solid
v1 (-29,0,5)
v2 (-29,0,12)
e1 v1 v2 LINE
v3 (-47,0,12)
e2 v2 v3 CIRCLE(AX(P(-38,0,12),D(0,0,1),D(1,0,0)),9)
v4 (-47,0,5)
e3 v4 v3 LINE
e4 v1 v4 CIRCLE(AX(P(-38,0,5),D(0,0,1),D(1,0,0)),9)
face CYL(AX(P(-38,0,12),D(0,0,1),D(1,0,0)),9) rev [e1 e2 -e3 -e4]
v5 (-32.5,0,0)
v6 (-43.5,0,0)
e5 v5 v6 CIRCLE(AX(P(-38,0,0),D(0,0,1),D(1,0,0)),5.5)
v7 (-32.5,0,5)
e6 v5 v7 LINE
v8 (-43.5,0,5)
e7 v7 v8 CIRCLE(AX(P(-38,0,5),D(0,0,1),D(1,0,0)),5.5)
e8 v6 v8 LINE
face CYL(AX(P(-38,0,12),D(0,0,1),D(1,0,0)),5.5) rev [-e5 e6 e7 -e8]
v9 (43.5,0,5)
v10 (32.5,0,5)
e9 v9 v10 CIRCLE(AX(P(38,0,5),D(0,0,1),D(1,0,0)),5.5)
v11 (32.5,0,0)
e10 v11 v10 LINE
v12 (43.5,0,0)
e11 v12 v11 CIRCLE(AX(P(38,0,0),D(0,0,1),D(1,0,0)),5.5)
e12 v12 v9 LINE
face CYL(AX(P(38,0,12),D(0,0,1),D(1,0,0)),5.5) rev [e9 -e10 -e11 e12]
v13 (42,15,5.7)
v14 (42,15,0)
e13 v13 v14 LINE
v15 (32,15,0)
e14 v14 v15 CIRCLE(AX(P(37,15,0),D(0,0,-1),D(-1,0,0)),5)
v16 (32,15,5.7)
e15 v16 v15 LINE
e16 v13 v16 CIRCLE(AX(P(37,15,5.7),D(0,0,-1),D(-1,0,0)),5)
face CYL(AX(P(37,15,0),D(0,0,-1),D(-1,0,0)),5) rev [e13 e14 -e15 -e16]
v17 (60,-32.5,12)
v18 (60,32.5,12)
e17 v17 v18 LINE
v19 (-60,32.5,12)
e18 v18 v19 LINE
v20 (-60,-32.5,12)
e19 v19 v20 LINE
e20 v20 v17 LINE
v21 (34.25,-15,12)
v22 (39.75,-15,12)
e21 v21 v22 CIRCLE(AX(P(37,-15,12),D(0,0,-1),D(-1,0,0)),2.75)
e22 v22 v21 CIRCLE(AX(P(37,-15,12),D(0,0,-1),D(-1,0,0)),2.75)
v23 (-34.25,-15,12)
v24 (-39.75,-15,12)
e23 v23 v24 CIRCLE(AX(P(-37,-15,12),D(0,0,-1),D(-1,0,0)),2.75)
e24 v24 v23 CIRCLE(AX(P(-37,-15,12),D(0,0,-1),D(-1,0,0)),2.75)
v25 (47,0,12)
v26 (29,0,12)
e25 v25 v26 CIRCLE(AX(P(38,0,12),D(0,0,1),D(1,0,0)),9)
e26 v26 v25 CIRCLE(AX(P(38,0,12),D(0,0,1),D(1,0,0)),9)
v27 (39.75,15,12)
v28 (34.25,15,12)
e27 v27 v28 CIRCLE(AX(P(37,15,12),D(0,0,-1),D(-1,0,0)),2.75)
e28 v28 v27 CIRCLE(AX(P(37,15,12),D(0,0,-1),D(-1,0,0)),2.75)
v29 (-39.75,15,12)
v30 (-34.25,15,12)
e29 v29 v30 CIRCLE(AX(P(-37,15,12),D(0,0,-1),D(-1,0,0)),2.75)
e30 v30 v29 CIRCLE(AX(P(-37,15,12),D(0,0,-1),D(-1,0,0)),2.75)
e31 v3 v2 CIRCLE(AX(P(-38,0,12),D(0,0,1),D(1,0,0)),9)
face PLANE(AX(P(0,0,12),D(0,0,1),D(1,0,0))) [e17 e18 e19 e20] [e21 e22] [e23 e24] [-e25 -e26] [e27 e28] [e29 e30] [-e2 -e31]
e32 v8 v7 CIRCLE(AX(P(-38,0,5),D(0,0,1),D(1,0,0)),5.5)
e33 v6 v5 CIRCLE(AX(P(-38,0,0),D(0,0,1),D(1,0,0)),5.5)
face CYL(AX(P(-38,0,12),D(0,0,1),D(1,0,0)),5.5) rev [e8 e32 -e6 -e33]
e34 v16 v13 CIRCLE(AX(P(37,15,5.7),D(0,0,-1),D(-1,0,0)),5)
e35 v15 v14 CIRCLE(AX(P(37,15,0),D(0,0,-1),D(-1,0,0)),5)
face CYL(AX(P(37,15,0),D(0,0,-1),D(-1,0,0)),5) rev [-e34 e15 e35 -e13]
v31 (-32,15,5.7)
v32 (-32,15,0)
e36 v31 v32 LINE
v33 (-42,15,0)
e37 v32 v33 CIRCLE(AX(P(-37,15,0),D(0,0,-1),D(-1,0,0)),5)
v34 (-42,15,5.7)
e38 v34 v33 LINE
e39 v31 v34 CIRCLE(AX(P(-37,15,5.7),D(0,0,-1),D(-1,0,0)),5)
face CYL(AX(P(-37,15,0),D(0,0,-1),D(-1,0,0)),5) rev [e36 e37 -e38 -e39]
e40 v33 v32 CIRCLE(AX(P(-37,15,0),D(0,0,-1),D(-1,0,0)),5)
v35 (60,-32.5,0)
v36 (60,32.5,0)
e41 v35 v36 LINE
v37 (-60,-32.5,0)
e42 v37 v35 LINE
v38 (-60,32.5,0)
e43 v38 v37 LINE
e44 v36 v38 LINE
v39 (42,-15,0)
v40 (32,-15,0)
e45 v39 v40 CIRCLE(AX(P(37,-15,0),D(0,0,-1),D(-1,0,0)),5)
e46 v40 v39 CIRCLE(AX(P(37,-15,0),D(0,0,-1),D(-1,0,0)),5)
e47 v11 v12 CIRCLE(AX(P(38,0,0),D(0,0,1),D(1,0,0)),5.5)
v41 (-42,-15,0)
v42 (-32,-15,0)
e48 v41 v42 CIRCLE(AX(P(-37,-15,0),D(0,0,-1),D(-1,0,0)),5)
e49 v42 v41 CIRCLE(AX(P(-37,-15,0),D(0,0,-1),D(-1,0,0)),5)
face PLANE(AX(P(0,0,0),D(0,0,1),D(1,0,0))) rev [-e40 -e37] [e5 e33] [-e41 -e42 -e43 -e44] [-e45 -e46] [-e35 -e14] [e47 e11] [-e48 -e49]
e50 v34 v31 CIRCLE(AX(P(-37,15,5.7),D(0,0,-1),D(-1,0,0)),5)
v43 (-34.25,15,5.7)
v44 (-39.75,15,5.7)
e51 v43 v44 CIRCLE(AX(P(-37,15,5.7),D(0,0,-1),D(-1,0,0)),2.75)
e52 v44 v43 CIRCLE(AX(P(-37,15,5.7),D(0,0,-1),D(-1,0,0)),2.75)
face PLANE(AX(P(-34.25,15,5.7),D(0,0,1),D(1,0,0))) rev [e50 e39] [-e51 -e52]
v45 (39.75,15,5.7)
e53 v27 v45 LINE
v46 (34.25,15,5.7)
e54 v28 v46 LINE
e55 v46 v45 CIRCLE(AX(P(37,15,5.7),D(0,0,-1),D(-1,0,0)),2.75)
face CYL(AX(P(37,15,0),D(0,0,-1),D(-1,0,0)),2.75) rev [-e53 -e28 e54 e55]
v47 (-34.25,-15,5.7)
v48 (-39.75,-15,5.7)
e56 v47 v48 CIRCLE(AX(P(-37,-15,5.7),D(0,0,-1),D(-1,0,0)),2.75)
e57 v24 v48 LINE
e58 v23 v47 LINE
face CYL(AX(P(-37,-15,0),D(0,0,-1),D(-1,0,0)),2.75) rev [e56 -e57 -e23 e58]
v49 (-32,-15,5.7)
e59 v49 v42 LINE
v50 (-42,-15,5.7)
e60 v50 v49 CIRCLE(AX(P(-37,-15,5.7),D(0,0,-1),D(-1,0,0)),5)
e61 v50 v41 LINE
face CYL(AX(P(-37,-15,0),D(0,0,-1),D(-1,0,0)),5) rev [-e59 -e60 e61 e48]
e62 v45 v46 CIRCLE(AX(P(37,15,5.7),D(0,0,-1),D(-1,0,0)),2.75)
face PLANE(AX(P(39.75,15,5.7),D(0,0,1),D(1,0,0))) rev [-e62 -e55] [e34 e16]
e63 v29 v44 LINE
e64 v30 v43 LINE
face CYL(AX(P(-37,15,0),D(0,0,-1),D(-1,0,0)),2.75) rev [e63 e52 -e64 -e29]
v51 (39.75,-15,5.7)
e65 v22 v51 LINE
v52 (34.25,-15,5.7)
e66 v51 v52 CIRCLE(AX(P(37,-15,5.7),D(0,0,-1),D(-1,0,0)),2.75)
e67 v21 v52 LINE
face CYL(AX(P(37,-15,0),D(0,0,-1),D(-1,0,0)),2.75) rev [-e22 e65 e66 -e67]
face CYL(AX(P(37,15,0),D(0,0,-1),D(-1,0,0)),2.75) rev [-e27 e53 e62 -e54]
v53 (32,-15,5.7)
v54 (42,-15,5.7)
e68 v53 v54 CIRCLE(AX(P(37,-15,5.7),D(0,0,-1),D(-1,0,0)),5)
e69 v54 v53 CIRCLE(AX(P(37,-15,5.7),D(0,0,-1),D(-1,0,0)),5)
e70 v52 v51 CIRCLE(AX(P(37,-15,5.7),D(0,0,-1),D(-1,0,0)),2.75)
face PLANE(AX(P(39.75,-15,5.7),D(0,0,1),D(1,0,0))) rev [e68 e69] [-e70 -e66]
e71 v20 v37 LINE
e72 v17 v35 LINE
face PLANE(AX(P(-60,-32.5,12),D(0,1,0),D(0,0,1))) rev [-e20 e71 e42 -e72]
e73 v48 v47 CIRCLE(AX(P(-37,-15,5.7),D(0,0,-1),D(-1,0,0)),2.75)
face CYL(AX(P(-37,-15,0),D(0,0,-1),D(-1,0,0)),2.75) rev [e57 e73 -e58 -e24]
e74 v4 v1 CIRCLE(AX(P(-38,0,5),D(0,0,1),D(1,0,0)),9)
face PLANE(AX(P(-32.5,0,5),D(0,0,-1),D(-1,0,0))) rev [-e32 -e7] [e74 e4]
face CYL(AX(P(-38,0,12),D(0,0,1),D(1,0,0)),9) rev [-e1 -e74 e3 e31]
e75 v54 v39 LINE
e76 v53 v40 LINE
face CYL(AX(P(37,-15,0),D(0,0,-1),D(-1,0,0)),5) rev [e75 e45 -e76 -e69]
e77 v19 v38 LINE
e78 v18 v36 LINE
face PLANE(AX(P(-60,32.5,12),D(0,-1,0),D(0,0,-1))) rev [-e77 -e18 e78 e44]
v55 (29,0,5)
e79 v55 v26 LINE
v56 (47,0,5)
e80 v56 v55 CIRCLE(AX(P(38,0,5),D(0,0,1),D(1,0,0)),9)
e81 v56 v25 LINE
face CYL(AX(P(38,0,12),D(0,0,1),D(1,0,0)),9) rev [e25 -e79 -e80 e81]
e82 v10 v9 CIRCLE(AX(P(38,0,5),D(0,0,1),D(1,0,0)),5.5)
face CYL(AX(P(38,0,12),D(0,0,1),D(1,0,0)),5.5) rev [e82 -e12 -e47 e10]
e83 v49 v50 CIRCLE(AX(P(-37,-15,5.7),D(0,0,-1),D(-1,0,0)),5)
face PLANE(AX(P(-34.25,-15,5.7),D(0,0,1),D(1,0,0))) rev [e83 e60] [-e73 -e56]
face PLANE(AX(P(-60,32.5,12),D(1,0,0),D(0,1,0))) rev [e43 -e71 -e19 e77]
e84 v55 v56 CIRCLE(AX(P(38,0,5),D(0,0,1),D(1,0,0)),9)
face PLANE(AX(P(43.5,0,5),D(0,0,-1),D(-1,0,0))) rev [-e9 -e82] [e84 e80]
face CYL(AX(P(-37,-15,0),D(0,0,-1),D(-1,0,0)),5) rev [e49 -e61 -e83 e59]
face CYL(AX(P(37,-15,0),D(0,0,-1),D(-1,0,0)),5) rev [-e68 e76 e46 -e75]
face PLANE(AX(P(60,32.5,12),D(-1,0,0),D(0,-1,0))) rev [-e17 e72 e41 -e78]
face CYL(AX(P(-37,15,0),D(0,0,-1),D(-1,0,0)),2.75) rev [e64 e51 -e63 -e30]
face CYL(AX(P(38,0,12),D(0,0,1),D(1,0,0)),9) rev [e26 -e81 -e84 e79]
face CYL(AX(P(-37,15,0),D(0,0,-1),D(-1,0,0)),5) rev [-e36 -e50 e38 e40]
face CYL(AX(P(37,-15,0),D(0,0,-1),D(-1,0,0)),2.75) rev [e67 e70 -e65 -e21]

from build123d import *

# Parameters (mm, degrees)
SKETCH1_W                                        = 120
SKETCH1_H                                        = 65
BOSS_EXTRUDE1_DEPTH                              = 12
HOLE_FOR_TORX_SOCKET_CAP_SCREW1_D                = 11
HOLE_FOR_TORX_SOCKET_CAP_SCREW1_CBORE_D          = 18
HOLE_FOR_TORX_SOCKET_CAP_SCREW1_CBORE_DEPTH      = 7
HOLE_FOR_SOCKET_HEAD_CAP_SCREW_TYPE2_D           = 5.5
HOLE_FOR_SOCKET_HEAD_CAP_SCREW_TYPE2_CBORE_D     = 10
HOLE_FOR_SOCKET_HEAD_CAP_SCREW_TYPE2_CBORE_DEPTH = 5.7


with BuildPart() as part:
    # Sketch1 → Boss-Extrude1 (new body)
    with BuildSketch(Plane.XY):
        Rectangle(SKETCH1_W, SKETCH1_H)
    extrude(amount=BOSS_EXTRUDE1_DEPTH)

    # Hole for Torx socket cap screw1 (through all)
    with Locations(Plane.XY.offset(12)):
        with Locations((-38, 0), (38, 0)):
            CounterBoreHole(HOLE_FOR_TORX_SOCKET_CAP_SCREW1_D / 2, HOLE_FOR_TORX_SOCKET_CAP_SCREW1_CBORE_D / 2, HOLE_FOR_TORX_SOCKET_CAP_SCREW1_CBORE_DEPTH)

    # Hole for socket head cap screw, type2 (through all)
    with Locations(Plane(origin=(0, 0, 0), x_dir=(-1, 0, 0), z_dir=(0, 0, -1))):
        with Locations((-37, 15), (-37, -15), (37, -15), (37, 15)):
            CounterBoreHole(HOLE_FOR_SOCKET_HEAD_CAP_SCREW_TYPE2_D / 2, HOLE_FOR_SOCKET_HEAD_CAP_SCREW_TYPE2_CBORE_D / 2, HOLE_FOR_SOCKET_HEAD_CAP_SCREW_TYPE2_CBORE_DEPTH)


solid = part.part
